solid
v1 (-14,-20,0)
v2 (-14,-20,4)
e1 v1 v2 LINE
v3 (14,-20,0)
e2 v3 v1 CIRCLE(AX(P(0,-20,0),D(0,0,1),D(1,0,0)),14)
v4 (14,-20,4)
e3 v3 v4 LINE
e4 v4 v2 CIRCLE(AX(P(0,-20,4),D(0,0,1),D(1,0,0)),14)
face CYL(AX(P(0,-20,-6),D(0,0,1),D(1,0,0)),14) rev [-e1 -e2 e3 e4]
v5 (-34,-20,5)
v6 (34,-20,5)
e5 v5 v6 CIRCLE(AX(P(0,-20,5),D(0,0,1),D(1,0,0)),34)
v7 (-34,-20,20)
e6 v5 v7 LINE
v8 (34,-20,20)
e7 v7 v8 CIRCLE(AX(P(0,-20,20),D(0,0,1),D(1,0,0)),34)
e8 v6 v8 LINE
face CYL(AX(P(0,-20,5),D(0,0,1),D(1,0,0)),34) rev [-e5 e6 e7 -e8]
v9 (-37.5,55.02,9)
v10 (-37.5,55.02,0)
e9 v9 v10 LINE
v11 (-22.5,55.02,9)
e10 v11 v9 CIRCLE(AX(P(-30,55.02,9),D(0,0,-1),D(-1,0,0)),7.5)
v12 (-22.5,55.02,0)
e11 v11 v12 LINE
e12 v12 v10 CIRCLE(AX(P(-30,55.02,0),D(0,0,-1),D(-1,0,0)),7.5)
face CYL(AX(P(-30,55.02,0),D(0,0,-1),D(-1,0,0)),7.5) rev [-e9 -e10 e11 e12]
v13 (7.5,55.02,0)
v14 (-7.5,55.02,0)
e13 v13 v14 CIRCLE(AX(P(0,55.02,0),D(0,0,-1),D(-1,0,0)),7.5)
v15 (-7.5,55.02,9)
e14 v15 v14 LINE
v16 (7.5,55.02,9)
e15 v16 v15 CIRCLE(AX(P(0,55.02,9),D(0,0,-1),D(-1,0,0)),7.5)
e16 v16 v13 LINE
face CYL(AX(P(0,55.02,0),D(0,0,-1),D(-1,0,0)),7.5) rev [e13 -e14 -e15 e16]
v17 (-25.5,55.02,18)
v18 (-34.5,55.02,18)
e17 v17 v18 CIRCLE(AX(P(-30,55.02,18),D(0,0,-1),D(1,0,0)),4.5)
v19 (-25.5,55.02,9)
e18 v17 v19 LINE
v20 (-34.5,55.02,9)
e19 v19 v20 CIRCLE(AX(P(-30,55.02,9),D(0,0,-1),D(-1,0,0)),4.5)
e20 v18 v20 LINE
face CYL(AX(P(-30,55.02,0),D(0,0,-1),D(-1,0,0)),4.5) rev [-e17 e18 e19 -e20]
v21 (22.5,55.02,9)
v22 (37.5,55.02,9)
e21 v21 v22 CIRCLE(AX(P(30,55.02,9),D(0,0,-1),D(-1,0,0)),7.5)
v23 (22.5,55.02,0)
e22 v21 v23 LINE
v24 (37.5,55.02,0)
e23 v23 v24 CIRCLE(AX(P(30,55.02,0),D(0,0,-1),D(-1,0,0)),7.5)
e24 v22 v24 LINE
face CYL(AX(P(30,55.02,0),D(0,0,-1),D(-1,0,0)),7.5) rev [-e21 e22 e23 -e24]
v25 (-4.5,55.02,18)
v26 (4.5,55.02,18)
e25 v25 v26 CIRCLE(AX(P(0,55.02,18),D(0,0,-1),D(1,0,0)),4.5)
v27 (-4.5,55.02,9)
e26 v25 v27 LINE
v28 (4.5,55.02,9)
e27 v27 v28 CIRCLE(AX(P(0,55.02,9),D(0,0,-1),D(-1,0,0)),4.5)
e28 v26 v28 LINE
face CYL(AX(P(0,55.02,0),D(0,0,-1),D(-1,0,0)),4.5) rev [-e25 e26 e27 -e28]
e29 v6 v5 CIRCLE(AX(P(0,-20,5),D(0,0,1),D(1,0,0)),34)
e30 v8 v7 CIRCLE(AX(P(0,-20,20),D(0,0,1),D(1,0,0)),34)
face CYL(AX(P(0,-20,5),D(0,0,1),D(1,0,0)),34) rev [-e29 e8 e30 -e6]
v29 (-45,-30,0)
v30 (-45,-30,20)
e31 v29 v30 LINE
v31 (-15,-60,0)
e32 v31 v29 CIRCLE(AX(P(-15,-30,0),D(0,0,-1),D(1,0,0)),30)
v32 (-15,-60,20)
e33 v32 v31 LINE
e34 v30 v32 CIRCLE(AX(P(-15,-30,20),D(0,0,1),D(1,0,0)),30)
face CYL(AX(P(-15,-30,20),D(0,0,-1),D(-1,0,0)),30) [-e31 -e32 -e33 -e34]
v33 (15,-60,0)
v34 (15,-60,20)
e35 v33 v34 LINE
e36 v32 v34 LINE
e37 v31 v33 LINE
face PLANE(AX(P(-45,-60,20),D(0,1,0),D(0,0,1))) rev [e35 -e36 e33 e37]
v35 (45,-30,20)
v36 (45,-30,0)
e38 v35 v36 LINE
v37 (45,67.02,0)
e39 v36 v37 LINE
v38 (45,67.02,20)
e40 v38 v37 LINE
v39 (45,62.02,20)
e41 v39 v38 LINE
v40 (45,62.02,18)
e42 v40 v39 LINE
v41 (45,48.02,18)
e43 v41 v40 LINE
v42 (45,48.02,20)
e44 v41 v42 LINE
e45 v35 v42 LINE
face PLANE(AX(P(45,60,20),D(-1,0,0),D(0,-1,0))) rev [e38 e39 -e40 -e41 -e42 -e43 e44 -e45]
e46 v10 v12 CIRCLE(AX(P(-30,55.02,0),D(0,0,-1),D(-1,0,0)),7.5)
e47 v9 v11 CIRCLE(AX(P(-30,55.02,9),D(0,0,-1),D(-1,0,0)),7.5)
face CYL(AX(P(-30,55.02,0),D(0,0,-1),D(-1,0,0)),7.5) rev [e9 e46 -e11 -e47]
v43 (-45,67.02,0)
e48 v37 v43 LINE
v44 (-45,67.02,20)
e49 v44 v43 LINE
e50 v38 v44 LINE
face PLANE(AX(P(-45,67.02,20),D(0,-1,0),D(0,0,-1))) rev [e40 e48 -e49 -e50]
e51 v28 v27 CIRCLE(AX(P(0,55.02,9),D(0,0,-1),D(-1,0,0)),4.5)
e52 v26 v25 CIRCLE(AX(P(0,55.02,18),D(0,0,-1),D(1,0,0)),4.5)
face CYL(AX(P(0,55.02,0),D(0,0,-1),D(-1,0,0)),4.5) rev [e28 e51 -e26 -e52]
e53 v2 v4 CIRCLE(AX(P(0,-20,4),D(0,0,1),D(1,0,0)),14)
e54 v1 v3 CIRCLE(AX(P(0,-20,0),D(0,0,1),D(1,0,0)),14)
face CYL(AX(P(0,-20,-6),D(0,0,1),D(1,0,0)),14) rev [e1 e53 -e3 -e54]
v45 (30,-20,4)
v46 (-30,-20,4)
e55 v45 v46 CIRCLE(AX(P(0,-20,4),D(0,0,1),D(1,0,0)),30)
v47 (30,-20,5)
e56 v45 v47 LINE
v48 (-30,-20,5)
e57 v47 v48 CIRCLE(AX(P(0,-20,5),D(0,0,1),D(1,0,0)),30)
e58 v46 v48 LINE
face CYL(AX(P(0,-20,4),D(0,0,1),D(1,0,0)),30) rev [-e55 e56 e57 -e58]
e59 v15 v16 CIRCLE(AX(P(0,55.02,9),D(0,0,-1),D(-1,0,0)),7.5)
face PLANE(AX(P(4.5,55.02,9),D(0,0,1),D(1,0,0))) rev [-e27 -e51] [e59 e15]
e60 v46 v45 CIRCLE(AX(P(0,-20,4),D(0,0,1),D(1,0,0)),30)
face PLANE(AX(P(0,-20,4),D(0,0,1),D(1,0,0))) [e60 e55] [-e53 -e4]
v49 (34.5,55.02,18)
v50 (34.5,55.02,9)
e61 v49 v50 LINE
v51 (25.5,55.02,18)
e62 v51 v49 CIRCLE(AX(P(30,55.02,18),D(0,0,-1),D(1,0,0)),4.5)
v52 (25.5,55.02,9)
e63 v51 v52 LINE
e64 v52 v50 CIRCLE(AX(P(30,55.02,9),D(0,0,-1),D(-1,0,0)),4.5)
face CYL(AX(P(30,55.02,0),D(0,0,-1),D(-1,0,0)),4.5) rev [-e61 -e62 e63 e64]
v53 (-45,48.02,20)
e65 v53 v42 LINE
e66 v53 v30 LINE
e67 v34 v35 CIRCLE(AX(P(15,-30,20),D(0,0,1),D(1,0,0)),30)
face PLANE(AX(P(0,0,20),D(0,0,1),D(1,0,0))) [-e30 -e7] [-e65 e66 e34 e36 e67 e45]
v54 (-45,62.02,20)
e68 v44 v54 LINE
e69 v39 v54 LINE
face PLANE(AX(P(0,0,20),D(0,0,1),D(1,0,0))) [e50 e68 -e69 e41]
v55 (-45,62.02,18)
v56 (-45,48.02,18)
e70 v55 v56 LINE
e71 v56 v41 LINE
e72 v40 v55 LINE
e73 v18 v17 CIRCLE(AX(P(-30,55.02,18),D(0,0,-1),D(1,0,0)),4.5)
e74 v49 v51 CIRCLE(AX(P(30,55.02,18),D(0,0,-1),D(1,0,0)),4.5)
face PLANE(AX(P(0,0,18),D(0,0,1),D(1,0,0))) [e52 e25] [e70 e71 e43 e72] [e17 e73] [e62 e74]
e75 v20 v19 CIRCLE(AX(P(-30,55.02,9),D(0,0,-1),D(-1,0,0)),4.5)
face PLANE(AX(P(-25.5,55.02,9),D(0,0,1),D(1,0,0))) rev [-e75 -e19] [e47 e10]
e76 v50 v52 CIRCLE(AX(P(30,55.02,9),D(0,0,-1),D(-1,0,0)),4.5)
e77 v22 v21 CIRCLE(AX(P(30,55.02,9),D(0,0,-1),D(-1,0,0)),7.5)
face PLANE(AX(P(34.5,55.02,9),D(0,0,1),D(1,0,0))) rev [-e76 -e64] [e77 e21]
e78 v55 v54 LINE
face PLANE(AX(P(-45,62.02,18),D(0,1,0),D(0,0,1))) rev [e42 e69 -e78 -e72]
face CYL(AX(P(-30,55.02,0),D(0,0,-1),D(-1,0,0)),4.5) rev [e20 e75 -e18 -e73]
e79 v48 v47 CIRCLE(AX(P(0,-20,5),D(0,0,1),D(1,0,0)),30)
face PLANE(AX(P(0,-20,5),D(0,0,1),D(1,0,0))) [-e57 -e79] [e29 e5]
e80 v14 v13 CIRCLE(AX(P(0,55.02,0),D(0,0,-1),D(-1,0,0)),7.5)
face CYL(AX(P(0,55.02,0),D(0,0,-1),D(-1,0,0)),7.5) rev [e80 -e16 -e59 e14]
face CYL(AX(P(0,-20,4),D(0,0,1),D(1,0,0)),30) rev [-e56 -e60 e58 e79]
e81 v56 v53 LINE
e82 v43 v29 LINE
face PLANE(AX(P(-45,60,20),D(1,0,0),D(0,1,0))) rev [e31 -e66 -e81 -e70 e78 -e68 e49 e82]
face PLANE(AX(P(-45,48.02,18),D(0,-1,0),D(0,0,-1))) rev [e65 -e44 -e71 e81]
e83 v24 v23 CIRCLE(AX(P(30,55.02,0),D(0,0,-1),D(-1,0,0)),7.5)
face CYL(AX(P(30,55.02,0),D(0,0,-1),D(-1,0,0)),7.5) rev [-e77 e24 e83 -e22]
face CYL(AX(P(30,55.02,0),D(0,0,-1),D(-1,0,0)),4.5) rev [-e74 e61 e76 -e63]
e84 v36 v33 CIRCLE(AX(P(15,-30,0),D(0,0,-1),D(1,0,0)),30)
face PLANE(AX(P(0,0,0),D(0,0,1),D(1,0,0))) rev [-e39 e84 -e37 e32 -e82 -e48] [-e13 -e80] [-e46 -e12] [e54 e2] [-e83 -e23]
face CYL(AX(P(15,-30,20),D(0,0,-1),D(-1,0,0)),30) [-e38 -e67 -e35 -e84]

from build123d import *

# Parameters (mm, degrees)
SKETCH1_W                                            = 90
SKETCH1_H                                            = 120
BOSS_EXTRUDE1_DEPTH                                  = 20
SKETCH2_R                                            = 34
CUT_EXTRUDE1_DEPTH                                   = 15
SKETCH3_R                                            = 30
CUT_EXTRUDE2_DEPTH                                   = 1
SKETCH4_R                                            = 14
CUT_EXTRUDE3_DEPTH                                   = 10
MOVE_FACE1_BY                                        = 2.02
FILLET1_R                                            = 30
MOVE_FACE2_BY                                        = 5
CBORE_FOR_M8_HEXAGON_SOCKET_HEAD_CAP_SCR_D           = 9
CBORE_FOR_M8_HEXAGON_SOCKET_HEAD_CAP_SCR_DEPTH       = 80.25
CBORE_FOR_M8_HEXAGON_SOCKET_HEAD_CAP_SCR_CBORE_D     = 15
CBORE_FOR_M8_HEXAGON_SOCKET_HEAD_CAP_SCR_CBORE_DEPTH = 9
CBORE_FOR_M8_HEXAGON_SOCKET_HEAD_CAP_SCR_TIP         = 2.703872786
SKETCH7_W                                            = 90
SKETCH7_H                                            = 14
CUT_EXTRUDE4_DEPTH                                   = 2


with BuildPart() as part:
    # Sketch1 → Boss-Extrude1 (new body)
    with BuildSketch(Plane.XY):
        Rectangle(SKETCH1_W, SKETCH1_H)
    extrude(amount=BOSS_EXTRUDE1_DEPTH)

    # Sketch2 → Cut-Extrude1 (cut)
    with BuildSketch(Plane.XY.offset(20)):
        with Locations((0, -20)):
            Circle(SKETCH2_R)
    extrude(amount=-CUT_EXTRUDE1_DEPTH, mode=Mode.SUBTRACT)

    # Sketch3 → Cut-Extrude2 (cut)
    with BuildSketch(Plane.XY.offset(5)):
        with Locations((0, -20)):
            Circle(SKETCH3_R)
    extrude(amount=-CUT_EXTRUDE2_DEPTH, mode=Mode.SUBTRACT)

    # Sketch4 → Cut-Extrude3 (cut)
    with BuildSketch(Plane.XY.offset(4)):
        with Locations((0, -20)):
            Circle(SKETCH4_R)
    extrude(amount=-CUT_EXTRUDE3_DEPTH, mode=Mode.SUBTRACT)

    # Move Face1: a face moved outward by 2.02
    extrude(part.faces().sort_by_distance((0, 60, 10))[0], amount=MOVE_FACE1_BY, dir=(0, 1, 0))

    # Fillet1
    fillet1_edges = [part.edges().sort_by_distance(p)[0] for p in [
        (45, -60, 10),
        (-45, -60, 10),
    ]]
    fillet(fillet1_edges, radius=FILLET1_R)

    # Move Face2: a face moved outward by 5.0
    extrude(part.faces().sort_by_distance((0, 62.02, 10))[0], amount=MOVE_FACE2_BY, dir=(0, 1, 0))

    # CBORE for M8 Hexagon socket head cap screws1
    with Locations(Plane(origin=(0, 0, 0), x_dir=(-1, 0, 0), z_dir=(0, 0, -1))):
        with Locations((30, 55.02), (-30, 55.02), (0, 55.02)):
            CounterBoreHole(CBORE_FOR_M8_HEXAGON_SOCKET_HEAD_CAP_SCR_D / 2, CBORE_FOR_M8_HEXAGON_SOCKET_HEAD_CAP_SCR_CBORE_D / 2, CBORE_FOR_M8_HEXAGON_SOCKET_HEAD_CAP_SCR_CBORE_DEPTH, depth=CBORE_FOR_M8_HEXAGON_SOCKET_HEAD_CAP_SCR_DEPTH)
            with Locations((0, 0, -(CBORE_FOR_M8_HEXAGON_SOCKET_HEAD_CAP_SCR_DEPTH + CBORE_FOR_M8_HEXAGON_SOCKET_HEAD_CAP_SCR_TIP / 2))):  # 118° drill point
                Cone(0, CBORE_FOR_M8_HEXAGON_SOCKET_HEAD_CAP_SCR_D / 2, CBORE_FOR_M8_HEXAGON_SOCKET_HEAD_CAP_SCR_TIP, mode=Mode.SUBTRACT)

    # Sketch7 → Cut-Extrude4 (cut)
    with BuildSketch(Plane.XY.offset(20)):
        with Locations((0, 55.02)):
            Rectangle(SKETCH7_W, SKETCH7_H)
    extrude(amount=-CUT_EXTRUDE4_DEPTH, mode=Mode.SUBTRACT)


solid = part.part
